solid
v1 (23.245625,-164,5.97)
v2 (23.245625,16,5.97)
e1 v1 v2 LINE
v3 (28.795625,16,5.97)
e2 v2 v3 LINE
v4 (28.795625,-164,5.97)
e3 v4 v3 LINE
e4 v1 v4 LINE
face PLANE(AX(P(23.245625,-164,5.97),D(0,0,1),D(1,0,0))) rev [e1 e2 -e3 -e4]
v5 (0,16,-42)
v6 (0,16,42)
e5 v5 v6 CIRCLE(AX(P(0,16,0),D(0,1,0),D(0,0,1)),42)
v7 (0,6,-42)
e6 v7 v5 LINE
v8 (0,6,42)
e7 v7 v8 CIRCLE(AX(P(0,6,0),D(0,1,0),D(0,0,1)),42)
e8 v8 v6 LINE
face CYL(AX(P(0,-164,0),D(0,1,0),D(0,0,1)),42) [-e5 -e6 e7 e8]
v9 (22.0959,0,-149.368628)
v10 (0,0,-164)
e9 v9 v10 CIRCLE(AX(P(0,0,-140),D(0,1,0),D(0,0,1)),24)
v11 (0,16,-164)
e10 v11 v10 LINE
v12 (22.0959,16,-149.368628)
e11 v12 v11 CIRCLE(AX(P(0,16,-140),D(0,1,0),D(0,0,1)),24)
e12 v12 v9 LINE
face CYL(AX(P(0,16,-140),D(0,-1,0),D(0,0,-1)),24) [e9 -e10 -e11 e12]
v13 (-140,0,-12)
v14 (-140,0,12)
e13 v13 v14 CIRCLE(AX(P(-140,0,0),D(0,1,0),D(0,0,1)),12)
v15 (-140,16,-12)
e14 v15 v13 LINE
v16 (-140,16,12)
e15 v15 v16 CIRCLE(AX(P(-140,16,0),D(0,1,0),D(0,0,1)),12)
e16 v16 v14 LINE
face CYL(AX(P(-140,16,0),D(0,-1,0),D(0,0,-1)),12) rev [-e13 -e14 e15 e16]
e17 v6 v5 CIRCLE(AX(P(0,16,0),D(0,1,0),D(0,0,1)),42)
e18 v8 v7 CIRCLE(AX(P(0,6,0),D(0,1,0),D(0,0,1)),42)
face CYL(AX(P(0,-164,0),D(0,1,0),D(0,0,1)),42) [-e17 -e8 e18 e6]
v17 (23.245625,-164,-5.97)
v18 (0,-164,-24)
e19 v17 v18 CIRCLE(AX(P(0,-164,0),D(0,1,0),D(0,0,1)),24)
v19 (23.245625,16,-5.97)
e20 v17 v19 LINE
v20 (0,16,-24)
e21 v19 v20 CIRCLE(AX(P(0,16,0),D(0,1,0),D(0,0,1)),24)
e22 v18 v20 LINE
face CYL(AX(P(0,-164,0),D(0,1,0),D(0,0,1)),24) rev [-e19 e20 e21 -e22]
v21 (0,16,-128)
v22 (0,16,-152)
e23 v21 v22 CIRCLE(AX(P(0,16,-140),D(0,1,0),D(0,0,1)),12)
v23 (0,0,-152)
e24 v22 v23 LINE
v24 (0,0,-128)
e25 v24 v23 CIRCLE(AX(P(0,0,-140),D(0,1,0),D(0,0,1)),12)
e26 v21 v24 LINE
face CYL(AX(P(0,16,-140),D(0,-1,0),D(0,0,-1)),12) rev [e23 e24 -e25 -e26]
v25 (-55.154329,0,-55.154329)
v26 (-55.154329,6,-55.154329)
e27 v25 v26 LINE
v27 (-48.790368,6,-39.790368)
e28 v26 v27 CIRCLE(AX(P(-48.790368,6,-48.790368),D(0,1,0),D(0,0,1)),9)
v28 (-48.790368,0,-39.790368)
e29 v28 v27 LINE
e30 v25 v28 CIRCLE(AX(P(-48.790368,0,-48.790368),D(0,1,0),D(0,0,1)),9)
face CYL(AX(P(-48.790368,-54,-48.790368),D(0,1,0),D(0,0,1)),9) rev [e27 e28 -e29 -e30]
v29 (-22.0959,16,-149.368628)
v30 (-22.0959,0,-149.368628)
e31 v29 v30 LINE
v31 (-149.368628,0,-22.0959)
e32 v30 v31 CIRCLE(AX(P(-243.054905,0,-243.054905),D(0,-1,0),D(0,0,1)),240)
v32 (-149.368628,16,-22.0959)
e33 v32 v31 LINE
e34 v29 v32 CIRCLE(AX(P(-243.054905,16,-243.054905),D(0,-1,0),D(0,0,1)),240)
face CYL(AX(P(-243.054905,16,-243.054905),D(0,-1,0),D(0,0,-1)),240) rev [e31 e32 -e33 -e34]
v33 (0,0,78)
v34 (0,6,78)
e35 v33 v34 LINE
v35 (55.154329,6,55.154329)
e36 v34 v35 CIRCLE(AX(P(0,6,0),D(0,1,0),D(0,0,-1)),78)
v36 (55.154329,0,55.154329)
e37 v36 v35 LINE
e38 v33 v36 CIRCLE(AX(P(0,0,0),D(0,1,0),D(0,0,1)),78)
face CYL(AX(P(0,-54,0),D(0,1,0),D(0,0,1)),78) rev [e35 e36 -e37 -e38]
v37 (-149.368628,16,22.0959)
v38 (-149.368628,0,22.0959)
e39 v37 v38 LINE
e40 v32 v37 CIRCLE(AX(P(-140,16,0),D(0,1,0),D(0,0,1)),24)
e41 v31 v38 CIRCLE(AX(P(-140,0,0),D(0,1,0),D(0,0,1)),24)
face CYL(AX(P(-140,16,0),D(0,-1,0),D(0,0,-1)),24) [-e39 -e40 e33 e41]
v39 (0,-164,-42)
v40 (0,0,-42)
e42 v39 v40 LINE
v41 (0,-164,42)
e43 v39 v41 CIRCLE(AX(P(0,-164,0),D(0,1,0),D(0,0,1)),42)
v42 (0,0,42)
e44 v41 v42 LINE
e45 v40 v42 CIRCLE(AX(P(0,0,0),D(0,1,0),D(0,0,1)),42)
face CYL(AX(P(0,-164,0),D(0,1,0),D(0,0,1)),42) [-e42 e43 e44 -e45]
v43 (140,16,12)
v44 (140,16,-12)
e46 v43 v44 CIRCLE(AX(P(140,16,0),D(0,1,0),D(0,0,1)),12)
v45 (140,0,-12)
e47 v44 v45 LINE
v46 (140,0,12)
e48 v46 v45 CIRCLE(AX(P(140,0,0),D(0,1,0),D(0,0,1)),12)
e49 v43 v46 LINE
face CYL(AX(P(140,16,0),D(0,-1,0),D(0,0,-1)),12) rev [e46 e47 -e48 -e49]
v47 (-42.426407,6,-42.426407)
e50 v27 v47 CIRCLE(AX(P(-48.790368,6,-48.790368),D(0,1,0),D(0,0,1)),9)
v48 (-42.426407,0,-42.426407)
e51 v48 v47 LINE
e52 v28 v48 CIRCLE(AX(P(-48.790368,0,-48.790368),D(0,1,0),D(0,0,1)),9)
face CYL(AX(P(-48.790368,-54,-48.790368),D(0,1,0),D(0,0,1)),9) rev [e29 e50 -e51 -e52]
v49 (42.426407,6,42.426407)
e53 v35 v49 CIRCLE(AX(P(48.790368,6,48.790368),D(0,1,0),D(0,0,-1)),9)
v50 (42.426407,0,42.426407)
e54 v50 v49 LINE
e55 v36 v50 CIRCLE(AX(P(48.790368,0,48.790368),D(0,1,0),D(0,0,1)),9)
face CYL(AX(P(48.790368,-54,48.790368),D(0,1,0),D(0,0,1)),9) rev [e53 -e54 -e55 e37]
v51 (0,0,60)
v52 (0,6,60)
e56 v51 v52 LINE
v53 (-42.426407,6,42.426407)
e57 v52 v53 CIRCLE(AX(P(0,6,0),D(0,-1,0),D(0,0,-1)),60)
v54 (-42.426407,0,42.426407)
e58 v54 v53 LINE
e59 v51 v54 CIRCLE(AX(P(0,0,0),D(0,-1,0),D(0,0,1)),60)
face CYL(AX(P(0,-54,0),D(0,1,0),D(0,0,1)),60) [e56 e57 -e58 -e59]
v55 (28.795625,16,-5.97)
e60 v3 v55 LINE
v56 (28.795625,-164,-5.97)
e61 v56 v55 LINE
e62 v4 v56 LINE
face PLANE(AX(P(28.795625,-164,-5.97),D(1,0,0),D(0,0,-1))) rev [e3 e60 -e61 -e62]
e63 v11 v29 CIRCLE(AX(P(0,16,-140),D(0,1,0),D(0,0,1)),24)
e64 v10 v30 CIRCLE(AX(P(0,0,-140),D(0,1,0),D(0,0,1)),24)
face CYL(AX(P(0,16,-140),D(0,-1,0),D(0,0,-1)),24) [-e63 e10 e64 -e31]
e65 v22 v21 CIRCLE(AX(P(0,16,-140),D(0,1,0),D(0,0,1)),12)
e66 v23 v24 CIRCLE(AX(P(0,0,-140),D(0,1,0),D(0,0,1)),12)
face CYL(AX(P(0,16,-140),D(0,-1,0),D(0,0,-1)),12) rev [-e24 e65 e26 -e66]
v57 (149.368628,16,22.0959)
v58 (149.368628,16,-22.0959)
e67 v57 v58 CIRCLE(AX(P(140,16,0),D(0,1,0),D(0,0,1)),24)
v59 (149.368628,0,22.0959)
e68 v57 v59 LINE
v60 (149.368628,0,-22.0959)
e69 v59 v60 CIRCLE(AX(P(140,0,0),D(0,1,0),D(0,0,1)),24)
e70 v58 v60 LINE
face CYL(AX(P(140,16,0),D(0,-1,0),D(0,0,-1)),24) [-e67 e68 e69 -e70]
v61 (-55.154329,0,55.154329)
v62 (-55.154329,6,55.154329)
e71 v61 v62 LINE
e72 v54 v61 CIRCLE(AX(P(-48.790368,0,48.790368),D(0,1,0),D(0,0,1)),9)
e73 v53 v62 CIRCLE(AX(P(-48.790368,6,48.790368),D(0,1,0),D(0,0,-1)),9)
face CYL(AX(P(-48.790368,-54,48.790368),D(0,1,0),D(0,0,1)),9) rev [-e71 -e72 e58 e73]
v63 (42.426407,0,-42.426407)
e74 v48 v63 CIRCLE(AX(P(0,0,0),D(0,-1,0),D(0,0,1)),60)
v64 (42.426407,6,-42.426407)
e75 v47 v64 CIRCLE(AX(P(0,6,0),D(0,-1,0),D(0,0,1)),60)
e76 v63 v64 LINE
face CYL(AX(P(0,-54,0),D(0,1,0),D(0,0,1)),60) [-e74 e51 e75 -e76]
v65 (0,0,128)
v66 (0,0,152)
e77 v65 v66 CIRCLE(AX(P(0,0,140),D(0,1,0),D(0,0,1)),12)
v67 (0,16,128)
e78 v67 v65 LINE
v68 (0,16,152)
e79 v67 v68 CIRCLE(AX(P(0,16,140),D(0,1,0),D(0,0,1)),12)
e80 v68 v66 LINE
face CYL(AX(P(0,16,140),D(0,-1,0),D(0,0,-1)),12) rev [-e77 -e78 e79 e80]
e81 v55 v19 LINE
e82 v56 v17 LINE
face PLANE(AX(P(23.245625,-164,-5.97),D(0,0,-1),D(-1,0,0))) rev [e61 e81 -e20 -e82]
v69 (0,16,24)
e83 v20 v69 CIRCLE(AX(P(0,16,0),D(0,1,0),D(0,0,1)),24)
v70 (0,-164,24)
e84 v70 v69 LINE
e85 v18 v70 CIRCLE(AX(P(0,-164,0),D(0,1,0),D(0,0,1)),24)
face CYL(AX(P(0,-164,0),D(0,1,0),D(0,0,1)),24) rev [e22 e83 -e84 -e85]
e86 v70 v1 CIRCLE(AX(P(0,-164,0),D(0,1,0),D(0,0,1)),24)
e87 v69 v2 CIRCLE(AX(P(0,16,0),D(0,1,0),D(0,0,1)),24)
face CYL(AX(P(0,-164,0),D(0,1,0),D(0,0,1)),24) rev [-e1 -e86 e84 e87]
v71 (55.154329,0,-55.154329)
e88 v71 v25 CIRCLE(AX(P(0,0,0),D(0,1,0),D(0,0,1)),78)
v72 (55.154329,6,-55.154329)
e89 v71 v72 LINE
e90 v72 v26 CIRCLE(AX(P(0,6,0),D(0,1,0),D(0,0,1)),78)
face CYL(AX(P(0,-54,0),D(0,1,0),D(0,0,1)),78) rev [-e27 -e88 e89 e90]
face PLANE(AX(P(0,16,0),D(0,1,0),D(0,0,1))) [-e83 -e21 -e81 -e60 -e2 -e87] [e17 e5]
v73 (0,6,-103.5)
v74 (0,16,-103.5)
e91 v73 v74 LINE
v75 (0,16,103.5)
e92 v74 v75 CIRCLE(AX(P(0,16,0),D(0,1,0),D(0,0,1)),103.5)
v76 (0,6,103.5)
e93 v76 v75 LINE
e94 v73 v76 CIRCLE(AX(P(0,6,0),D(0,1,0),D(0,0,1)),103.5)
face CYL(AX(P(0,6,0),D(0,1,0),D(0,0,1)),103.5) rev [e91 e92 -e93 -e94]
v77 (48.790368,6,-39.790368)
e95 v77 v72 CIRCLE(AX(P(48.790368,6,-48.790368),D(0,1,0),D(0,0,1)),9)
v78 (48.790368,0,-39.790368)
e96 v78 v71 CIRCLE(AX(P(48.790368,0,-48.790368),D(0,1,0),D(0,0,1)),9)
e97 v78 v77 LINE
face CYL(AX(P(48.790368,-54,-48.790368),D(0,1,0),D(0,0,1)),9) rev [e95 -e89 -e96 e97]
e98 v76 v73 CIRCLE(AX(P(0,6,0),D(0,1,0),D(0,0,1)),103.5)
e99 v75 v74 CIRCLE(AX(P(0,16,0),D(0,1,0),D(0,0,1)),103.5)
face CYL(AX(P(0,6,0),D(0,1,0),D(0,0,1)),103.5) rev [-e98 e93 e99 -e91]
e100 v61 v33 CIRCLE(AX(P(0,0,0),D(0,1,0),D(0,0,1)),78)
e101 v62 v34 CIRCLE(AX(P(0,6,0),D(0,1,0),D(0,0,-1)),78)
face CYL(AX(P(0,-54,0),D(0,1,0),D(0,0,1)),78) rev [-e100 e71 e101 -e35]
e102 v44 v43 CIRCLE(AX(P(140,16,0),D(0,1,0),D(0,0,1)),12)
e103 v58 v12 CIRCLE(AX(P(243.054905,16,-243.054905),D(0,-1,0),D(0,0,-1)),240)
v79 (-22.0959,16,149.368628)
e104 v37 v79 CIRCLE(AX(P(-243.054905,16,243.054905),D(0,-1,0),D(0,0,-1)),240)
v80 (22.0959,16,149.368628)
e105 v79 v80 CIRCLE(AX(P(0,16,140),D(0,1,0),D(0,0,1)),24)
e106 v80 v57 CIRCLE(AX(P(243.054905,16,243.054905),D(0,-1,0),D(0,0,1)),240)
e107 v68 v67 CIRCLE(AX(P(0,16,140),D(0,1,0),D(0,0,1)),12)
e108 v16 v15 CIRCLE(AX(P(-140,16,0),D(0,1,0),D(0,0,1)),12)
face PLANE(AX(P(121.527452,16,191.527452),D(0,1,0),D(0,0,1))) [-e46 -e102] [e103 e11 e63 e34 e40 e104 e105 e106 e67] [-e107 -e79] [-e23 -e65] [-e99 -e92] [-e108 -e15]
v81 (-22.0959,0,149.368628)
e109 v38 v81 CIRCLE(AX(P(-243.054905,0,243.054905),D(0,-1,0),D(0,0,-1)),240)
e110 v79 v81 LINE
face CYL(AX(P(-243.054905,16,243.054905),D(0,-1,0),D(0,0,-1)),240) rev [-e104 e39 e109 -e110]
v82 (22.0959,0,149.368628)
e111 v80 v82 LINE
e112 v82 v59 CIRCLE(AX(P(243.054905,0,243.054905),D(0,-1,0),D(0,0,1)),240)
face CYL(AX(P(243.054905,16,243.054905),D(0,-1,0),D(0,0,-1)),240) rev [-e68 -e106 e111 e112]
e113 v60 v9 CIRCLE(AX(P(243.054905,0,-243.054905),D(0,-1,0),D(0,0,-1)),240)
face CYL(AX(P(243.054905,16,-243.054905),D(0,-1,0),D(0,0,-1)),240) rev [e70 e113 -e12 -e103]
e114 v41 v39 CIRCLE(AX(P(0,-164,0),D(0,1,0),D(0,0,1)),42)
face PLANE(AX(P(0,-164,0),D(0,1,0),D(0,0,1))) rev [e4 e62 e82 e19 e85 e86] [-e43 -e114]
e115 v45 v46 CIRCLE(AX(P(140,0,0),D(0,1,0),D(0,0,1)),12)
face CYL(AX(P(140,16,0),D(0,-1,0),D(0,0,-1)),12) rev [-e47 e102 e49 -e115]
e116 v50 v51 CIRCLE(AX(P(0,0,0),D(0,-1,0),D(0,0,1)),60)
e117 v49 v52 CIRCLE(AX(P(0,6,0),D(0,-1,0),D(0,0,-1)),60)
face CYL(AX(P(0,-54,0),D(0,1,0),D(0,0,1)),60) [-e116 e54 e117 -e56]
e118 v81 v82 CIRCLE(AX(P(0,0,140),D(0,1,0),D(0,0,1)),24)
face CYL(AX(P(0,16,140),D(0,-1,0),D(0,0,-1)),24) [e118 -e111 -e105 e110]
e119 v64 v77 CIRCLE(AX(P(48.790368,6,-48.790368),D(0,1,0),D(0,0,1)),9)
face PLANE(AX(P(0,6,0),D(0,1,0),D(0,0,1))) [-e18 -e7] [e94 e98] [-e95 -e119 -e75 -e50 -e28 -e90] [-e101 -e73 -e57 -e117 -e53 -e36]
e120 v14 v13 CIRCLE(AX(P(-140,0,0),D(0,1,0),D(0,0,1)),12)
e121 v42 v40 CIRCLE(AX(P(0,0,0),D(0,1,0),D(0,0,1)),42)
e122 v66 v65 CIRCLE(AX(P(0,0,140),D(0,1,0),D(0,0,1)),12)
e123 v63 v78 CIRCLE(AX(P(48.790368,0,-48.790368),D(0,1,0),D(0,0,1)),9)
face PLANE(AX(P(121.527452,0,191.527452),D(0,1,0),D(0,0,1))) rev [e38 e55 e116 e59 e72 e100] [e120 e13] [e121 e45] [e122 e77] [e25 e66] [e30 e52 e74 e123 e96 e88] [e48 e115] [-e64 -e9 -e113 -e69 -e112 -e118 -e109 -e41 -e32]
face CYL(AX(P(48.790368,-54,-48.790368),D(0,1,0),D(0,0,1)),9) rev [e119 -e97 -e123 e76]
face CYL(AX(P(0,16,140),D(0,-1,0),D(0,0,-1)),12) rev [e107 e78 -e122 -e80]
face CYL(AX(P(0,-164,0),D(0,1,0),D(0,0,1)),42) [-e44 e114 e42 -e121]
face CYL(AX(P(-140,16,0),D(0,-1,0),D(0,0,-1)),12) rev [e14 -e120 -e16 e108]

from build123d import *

# Parameters (mm, degrees)
SQUARE_FLANGE_PROFILE_SKETCH_R = 12
SQUARE_FLANGE_240X16_DEPTH     = 16
FLANGE_STEP_CIRCLE_SKETCH_R    = 103.5
FLANGE_STEP_CUT_207_DEPTH      = 10
ARC_SLOTS_R78_DEPTH            = 60
HUB_SKETCH_R                   = 42
HUB_84_DEPTH                   = 180
BORE_SKETCH_R                  = 24
BORE_48_DEPTH                  = 180
KEYWAY_SKETCH_W                = 5.55
KEYWAY_SKETCH_H                = 11.94
KEYWAY_DEPTH                   = 180


with BuildPart() as part:
    # Square Flange Profile Sketch → Square Flange 240x16 (new body)
    with BuildSketch(Plane(origin=(0, 0, 0), x_dir=(1, 0, 0), z_dir=(0, 1, 0))):
        with BuildLine():
            ThreePointArc((22.095900417, 149.368627689), (0, 164), (-22.095900417, 149.368627689))
            ThreePointArc((-22.095900417, 149.368627689), (-73.349277098, 73.349277098), (-149.368627689, 22.095900417))
            ThreePointArc((-149.368627689, 22.095900417), (-164, 0), (-149.368627689, -22.095900417))
            ThreePointArc((-149.368627689, -22.095900417), (-73.349277098, -73.349277098), (-22.095900417, -149.368627689))
            ThreePointArc((-22.095900417, -149.368627689), (0, -164), (22.095900417, -149.368627689))
            ThreePointArc((22.095900417, -149.368627689), (73.349277098, -73.349277098), (149.368627689, -22.095900417))
            ThreePointArc((149.368627689, -22.095900417), (164, 0), (149.368627689, 22.095900417))
            ThreePointArc((149.368627689, 22.095900417), (73.349277098, 73.349277098), (22.095900417, 149.368627689))
        make_face()
        with Locations(Location((0, 140, 0), (0, 0, 270))):
            Circle(SQUARE_FLANGE_PROFILE_SKETCH_R, mode=Mode.SUBTRACT)
        with Locations(Location((140, 0, 0), (0, 0, 270))):
            Circle(SQUARE_FLANGE_PROFILE_SKETCH_R, mode=Mode.SUBTRACT)
        with Locations(Location((0, -140, 0), (0, 0, 270))):
            Circle(SQUARE_FLANGE_PROFILE_SKETCH_R, mode=Mode.SUBTRACT)
        with Locations(Location((-140, 0, 0), (0, 0, 270))):
            Circle(SQUARE_FLANGE_PROFILE_SKETCH_R, mode=Mode.SUBTRACT)
    extrude(amount=SQUARE_FLANGE_240X16_DEPTH)

    # Flange Step Circle Sketch → Flange Step Cut Ø207 (cut)
    with BuildSketch(Plane(origin=(0, 16, 0), x_dir=(1, 0, 0), z_dir=(0, 1, 0))):
        with Locations(Location((0, 0, 0), (0, 0, 270))):
            Circle(FLANGE_STEP_CIRCLE_SKETCH_R)
    extrude(amount=-FLANGE_STEP_CUT_207_DEPTH, mode=Mode.SUBTRACT)

    # Arc Slots Sketch → Arc Slots R78 (cut)
    with BuildSketch(Plane(origin=(0, 6, 0), x_dir=(1, 0, 0), z_dir=(0, 1, 0))):
        with BuildLine():
            ThreePointArc((55.154328933, 55.154328933), (0, 78), (-55.154328933, 55.154328933))
            ThreePointArc((-55.154328933, 55.154328933), (-55.154328933, 42.426406871), (-42.426406871, 42.426406871))
            ThreePointArc((-42.426406871, 42.426406871), (0, 60), (42.426406871, 42.426406871))
            ThreePointArc((42.426406871, 42.426406871), (55.154328933, 42.426406871), (55.154328933, 55.154328933))
        make_face()
        with BuildLine():
            ThreePointArc((42.426406871, -42.426406871), (0, -60), (-42.426406871, -42.426406871))
            ThreePointArc((-42.426406871, -42.426406871), (-55.154328933, -42.426406871), (-55.154328933, -55.154328933))
            ThreePointArc((-55.154328933, -55.154328933), (0, -78), (55.154328933, -55.154328933))
            ThreePointArc((55.154328933, -55.154328933), (55.154328933, -42.426406871), (42.426406871, -42.426406871))
        make_face()
    extrude(amount=-ARC_SLOTS_R78_DEPTH, mode=Mode.SUBTRACT)

    # Hub Sketch → Hub Ø84 (add)
    with BuildSketch(Plane(origin=(0, 16, 0), x_dir=(1, 0, 0), z_dir=(0, 1, 0))):
        with Locations(Location((0, 0, 0), (0, 0, 270))):
            Circle(HUB_SKETCH_R)
    extrude(amount=-HUB_84_DEPTH)

    # Bore Sketch → Bore Ø48 (cut)
    with BuildSketch(Plane(origin=(0, 16, 0), x_dir=(1, 0, 0), z_dir=(0, 1, 0))):
        with Locations(Location((0, 0, 0), (0, 0, 270))):
            Circle(BORE_SKETCH_R)
    extrude(amount=-BORE_48_DEPTH, mode=Mode.SUBTRACT)

    # Keyway Sketch → Keyway (cut)
    with BuildSketch(Plane(origin=(0, 16, 0), x_dir=(1, 0, 0), z_dir=(0, 1, 0))):
        with Locations((26.020625395, 0)):
            Rectangle(KEYWAY_SKETCH_W, KEYWAY_SKETCH_H)
    extrude(amount=-KEYWAY_DEPTH, mode=Mode.SUBTRACT)


solid = part.part
